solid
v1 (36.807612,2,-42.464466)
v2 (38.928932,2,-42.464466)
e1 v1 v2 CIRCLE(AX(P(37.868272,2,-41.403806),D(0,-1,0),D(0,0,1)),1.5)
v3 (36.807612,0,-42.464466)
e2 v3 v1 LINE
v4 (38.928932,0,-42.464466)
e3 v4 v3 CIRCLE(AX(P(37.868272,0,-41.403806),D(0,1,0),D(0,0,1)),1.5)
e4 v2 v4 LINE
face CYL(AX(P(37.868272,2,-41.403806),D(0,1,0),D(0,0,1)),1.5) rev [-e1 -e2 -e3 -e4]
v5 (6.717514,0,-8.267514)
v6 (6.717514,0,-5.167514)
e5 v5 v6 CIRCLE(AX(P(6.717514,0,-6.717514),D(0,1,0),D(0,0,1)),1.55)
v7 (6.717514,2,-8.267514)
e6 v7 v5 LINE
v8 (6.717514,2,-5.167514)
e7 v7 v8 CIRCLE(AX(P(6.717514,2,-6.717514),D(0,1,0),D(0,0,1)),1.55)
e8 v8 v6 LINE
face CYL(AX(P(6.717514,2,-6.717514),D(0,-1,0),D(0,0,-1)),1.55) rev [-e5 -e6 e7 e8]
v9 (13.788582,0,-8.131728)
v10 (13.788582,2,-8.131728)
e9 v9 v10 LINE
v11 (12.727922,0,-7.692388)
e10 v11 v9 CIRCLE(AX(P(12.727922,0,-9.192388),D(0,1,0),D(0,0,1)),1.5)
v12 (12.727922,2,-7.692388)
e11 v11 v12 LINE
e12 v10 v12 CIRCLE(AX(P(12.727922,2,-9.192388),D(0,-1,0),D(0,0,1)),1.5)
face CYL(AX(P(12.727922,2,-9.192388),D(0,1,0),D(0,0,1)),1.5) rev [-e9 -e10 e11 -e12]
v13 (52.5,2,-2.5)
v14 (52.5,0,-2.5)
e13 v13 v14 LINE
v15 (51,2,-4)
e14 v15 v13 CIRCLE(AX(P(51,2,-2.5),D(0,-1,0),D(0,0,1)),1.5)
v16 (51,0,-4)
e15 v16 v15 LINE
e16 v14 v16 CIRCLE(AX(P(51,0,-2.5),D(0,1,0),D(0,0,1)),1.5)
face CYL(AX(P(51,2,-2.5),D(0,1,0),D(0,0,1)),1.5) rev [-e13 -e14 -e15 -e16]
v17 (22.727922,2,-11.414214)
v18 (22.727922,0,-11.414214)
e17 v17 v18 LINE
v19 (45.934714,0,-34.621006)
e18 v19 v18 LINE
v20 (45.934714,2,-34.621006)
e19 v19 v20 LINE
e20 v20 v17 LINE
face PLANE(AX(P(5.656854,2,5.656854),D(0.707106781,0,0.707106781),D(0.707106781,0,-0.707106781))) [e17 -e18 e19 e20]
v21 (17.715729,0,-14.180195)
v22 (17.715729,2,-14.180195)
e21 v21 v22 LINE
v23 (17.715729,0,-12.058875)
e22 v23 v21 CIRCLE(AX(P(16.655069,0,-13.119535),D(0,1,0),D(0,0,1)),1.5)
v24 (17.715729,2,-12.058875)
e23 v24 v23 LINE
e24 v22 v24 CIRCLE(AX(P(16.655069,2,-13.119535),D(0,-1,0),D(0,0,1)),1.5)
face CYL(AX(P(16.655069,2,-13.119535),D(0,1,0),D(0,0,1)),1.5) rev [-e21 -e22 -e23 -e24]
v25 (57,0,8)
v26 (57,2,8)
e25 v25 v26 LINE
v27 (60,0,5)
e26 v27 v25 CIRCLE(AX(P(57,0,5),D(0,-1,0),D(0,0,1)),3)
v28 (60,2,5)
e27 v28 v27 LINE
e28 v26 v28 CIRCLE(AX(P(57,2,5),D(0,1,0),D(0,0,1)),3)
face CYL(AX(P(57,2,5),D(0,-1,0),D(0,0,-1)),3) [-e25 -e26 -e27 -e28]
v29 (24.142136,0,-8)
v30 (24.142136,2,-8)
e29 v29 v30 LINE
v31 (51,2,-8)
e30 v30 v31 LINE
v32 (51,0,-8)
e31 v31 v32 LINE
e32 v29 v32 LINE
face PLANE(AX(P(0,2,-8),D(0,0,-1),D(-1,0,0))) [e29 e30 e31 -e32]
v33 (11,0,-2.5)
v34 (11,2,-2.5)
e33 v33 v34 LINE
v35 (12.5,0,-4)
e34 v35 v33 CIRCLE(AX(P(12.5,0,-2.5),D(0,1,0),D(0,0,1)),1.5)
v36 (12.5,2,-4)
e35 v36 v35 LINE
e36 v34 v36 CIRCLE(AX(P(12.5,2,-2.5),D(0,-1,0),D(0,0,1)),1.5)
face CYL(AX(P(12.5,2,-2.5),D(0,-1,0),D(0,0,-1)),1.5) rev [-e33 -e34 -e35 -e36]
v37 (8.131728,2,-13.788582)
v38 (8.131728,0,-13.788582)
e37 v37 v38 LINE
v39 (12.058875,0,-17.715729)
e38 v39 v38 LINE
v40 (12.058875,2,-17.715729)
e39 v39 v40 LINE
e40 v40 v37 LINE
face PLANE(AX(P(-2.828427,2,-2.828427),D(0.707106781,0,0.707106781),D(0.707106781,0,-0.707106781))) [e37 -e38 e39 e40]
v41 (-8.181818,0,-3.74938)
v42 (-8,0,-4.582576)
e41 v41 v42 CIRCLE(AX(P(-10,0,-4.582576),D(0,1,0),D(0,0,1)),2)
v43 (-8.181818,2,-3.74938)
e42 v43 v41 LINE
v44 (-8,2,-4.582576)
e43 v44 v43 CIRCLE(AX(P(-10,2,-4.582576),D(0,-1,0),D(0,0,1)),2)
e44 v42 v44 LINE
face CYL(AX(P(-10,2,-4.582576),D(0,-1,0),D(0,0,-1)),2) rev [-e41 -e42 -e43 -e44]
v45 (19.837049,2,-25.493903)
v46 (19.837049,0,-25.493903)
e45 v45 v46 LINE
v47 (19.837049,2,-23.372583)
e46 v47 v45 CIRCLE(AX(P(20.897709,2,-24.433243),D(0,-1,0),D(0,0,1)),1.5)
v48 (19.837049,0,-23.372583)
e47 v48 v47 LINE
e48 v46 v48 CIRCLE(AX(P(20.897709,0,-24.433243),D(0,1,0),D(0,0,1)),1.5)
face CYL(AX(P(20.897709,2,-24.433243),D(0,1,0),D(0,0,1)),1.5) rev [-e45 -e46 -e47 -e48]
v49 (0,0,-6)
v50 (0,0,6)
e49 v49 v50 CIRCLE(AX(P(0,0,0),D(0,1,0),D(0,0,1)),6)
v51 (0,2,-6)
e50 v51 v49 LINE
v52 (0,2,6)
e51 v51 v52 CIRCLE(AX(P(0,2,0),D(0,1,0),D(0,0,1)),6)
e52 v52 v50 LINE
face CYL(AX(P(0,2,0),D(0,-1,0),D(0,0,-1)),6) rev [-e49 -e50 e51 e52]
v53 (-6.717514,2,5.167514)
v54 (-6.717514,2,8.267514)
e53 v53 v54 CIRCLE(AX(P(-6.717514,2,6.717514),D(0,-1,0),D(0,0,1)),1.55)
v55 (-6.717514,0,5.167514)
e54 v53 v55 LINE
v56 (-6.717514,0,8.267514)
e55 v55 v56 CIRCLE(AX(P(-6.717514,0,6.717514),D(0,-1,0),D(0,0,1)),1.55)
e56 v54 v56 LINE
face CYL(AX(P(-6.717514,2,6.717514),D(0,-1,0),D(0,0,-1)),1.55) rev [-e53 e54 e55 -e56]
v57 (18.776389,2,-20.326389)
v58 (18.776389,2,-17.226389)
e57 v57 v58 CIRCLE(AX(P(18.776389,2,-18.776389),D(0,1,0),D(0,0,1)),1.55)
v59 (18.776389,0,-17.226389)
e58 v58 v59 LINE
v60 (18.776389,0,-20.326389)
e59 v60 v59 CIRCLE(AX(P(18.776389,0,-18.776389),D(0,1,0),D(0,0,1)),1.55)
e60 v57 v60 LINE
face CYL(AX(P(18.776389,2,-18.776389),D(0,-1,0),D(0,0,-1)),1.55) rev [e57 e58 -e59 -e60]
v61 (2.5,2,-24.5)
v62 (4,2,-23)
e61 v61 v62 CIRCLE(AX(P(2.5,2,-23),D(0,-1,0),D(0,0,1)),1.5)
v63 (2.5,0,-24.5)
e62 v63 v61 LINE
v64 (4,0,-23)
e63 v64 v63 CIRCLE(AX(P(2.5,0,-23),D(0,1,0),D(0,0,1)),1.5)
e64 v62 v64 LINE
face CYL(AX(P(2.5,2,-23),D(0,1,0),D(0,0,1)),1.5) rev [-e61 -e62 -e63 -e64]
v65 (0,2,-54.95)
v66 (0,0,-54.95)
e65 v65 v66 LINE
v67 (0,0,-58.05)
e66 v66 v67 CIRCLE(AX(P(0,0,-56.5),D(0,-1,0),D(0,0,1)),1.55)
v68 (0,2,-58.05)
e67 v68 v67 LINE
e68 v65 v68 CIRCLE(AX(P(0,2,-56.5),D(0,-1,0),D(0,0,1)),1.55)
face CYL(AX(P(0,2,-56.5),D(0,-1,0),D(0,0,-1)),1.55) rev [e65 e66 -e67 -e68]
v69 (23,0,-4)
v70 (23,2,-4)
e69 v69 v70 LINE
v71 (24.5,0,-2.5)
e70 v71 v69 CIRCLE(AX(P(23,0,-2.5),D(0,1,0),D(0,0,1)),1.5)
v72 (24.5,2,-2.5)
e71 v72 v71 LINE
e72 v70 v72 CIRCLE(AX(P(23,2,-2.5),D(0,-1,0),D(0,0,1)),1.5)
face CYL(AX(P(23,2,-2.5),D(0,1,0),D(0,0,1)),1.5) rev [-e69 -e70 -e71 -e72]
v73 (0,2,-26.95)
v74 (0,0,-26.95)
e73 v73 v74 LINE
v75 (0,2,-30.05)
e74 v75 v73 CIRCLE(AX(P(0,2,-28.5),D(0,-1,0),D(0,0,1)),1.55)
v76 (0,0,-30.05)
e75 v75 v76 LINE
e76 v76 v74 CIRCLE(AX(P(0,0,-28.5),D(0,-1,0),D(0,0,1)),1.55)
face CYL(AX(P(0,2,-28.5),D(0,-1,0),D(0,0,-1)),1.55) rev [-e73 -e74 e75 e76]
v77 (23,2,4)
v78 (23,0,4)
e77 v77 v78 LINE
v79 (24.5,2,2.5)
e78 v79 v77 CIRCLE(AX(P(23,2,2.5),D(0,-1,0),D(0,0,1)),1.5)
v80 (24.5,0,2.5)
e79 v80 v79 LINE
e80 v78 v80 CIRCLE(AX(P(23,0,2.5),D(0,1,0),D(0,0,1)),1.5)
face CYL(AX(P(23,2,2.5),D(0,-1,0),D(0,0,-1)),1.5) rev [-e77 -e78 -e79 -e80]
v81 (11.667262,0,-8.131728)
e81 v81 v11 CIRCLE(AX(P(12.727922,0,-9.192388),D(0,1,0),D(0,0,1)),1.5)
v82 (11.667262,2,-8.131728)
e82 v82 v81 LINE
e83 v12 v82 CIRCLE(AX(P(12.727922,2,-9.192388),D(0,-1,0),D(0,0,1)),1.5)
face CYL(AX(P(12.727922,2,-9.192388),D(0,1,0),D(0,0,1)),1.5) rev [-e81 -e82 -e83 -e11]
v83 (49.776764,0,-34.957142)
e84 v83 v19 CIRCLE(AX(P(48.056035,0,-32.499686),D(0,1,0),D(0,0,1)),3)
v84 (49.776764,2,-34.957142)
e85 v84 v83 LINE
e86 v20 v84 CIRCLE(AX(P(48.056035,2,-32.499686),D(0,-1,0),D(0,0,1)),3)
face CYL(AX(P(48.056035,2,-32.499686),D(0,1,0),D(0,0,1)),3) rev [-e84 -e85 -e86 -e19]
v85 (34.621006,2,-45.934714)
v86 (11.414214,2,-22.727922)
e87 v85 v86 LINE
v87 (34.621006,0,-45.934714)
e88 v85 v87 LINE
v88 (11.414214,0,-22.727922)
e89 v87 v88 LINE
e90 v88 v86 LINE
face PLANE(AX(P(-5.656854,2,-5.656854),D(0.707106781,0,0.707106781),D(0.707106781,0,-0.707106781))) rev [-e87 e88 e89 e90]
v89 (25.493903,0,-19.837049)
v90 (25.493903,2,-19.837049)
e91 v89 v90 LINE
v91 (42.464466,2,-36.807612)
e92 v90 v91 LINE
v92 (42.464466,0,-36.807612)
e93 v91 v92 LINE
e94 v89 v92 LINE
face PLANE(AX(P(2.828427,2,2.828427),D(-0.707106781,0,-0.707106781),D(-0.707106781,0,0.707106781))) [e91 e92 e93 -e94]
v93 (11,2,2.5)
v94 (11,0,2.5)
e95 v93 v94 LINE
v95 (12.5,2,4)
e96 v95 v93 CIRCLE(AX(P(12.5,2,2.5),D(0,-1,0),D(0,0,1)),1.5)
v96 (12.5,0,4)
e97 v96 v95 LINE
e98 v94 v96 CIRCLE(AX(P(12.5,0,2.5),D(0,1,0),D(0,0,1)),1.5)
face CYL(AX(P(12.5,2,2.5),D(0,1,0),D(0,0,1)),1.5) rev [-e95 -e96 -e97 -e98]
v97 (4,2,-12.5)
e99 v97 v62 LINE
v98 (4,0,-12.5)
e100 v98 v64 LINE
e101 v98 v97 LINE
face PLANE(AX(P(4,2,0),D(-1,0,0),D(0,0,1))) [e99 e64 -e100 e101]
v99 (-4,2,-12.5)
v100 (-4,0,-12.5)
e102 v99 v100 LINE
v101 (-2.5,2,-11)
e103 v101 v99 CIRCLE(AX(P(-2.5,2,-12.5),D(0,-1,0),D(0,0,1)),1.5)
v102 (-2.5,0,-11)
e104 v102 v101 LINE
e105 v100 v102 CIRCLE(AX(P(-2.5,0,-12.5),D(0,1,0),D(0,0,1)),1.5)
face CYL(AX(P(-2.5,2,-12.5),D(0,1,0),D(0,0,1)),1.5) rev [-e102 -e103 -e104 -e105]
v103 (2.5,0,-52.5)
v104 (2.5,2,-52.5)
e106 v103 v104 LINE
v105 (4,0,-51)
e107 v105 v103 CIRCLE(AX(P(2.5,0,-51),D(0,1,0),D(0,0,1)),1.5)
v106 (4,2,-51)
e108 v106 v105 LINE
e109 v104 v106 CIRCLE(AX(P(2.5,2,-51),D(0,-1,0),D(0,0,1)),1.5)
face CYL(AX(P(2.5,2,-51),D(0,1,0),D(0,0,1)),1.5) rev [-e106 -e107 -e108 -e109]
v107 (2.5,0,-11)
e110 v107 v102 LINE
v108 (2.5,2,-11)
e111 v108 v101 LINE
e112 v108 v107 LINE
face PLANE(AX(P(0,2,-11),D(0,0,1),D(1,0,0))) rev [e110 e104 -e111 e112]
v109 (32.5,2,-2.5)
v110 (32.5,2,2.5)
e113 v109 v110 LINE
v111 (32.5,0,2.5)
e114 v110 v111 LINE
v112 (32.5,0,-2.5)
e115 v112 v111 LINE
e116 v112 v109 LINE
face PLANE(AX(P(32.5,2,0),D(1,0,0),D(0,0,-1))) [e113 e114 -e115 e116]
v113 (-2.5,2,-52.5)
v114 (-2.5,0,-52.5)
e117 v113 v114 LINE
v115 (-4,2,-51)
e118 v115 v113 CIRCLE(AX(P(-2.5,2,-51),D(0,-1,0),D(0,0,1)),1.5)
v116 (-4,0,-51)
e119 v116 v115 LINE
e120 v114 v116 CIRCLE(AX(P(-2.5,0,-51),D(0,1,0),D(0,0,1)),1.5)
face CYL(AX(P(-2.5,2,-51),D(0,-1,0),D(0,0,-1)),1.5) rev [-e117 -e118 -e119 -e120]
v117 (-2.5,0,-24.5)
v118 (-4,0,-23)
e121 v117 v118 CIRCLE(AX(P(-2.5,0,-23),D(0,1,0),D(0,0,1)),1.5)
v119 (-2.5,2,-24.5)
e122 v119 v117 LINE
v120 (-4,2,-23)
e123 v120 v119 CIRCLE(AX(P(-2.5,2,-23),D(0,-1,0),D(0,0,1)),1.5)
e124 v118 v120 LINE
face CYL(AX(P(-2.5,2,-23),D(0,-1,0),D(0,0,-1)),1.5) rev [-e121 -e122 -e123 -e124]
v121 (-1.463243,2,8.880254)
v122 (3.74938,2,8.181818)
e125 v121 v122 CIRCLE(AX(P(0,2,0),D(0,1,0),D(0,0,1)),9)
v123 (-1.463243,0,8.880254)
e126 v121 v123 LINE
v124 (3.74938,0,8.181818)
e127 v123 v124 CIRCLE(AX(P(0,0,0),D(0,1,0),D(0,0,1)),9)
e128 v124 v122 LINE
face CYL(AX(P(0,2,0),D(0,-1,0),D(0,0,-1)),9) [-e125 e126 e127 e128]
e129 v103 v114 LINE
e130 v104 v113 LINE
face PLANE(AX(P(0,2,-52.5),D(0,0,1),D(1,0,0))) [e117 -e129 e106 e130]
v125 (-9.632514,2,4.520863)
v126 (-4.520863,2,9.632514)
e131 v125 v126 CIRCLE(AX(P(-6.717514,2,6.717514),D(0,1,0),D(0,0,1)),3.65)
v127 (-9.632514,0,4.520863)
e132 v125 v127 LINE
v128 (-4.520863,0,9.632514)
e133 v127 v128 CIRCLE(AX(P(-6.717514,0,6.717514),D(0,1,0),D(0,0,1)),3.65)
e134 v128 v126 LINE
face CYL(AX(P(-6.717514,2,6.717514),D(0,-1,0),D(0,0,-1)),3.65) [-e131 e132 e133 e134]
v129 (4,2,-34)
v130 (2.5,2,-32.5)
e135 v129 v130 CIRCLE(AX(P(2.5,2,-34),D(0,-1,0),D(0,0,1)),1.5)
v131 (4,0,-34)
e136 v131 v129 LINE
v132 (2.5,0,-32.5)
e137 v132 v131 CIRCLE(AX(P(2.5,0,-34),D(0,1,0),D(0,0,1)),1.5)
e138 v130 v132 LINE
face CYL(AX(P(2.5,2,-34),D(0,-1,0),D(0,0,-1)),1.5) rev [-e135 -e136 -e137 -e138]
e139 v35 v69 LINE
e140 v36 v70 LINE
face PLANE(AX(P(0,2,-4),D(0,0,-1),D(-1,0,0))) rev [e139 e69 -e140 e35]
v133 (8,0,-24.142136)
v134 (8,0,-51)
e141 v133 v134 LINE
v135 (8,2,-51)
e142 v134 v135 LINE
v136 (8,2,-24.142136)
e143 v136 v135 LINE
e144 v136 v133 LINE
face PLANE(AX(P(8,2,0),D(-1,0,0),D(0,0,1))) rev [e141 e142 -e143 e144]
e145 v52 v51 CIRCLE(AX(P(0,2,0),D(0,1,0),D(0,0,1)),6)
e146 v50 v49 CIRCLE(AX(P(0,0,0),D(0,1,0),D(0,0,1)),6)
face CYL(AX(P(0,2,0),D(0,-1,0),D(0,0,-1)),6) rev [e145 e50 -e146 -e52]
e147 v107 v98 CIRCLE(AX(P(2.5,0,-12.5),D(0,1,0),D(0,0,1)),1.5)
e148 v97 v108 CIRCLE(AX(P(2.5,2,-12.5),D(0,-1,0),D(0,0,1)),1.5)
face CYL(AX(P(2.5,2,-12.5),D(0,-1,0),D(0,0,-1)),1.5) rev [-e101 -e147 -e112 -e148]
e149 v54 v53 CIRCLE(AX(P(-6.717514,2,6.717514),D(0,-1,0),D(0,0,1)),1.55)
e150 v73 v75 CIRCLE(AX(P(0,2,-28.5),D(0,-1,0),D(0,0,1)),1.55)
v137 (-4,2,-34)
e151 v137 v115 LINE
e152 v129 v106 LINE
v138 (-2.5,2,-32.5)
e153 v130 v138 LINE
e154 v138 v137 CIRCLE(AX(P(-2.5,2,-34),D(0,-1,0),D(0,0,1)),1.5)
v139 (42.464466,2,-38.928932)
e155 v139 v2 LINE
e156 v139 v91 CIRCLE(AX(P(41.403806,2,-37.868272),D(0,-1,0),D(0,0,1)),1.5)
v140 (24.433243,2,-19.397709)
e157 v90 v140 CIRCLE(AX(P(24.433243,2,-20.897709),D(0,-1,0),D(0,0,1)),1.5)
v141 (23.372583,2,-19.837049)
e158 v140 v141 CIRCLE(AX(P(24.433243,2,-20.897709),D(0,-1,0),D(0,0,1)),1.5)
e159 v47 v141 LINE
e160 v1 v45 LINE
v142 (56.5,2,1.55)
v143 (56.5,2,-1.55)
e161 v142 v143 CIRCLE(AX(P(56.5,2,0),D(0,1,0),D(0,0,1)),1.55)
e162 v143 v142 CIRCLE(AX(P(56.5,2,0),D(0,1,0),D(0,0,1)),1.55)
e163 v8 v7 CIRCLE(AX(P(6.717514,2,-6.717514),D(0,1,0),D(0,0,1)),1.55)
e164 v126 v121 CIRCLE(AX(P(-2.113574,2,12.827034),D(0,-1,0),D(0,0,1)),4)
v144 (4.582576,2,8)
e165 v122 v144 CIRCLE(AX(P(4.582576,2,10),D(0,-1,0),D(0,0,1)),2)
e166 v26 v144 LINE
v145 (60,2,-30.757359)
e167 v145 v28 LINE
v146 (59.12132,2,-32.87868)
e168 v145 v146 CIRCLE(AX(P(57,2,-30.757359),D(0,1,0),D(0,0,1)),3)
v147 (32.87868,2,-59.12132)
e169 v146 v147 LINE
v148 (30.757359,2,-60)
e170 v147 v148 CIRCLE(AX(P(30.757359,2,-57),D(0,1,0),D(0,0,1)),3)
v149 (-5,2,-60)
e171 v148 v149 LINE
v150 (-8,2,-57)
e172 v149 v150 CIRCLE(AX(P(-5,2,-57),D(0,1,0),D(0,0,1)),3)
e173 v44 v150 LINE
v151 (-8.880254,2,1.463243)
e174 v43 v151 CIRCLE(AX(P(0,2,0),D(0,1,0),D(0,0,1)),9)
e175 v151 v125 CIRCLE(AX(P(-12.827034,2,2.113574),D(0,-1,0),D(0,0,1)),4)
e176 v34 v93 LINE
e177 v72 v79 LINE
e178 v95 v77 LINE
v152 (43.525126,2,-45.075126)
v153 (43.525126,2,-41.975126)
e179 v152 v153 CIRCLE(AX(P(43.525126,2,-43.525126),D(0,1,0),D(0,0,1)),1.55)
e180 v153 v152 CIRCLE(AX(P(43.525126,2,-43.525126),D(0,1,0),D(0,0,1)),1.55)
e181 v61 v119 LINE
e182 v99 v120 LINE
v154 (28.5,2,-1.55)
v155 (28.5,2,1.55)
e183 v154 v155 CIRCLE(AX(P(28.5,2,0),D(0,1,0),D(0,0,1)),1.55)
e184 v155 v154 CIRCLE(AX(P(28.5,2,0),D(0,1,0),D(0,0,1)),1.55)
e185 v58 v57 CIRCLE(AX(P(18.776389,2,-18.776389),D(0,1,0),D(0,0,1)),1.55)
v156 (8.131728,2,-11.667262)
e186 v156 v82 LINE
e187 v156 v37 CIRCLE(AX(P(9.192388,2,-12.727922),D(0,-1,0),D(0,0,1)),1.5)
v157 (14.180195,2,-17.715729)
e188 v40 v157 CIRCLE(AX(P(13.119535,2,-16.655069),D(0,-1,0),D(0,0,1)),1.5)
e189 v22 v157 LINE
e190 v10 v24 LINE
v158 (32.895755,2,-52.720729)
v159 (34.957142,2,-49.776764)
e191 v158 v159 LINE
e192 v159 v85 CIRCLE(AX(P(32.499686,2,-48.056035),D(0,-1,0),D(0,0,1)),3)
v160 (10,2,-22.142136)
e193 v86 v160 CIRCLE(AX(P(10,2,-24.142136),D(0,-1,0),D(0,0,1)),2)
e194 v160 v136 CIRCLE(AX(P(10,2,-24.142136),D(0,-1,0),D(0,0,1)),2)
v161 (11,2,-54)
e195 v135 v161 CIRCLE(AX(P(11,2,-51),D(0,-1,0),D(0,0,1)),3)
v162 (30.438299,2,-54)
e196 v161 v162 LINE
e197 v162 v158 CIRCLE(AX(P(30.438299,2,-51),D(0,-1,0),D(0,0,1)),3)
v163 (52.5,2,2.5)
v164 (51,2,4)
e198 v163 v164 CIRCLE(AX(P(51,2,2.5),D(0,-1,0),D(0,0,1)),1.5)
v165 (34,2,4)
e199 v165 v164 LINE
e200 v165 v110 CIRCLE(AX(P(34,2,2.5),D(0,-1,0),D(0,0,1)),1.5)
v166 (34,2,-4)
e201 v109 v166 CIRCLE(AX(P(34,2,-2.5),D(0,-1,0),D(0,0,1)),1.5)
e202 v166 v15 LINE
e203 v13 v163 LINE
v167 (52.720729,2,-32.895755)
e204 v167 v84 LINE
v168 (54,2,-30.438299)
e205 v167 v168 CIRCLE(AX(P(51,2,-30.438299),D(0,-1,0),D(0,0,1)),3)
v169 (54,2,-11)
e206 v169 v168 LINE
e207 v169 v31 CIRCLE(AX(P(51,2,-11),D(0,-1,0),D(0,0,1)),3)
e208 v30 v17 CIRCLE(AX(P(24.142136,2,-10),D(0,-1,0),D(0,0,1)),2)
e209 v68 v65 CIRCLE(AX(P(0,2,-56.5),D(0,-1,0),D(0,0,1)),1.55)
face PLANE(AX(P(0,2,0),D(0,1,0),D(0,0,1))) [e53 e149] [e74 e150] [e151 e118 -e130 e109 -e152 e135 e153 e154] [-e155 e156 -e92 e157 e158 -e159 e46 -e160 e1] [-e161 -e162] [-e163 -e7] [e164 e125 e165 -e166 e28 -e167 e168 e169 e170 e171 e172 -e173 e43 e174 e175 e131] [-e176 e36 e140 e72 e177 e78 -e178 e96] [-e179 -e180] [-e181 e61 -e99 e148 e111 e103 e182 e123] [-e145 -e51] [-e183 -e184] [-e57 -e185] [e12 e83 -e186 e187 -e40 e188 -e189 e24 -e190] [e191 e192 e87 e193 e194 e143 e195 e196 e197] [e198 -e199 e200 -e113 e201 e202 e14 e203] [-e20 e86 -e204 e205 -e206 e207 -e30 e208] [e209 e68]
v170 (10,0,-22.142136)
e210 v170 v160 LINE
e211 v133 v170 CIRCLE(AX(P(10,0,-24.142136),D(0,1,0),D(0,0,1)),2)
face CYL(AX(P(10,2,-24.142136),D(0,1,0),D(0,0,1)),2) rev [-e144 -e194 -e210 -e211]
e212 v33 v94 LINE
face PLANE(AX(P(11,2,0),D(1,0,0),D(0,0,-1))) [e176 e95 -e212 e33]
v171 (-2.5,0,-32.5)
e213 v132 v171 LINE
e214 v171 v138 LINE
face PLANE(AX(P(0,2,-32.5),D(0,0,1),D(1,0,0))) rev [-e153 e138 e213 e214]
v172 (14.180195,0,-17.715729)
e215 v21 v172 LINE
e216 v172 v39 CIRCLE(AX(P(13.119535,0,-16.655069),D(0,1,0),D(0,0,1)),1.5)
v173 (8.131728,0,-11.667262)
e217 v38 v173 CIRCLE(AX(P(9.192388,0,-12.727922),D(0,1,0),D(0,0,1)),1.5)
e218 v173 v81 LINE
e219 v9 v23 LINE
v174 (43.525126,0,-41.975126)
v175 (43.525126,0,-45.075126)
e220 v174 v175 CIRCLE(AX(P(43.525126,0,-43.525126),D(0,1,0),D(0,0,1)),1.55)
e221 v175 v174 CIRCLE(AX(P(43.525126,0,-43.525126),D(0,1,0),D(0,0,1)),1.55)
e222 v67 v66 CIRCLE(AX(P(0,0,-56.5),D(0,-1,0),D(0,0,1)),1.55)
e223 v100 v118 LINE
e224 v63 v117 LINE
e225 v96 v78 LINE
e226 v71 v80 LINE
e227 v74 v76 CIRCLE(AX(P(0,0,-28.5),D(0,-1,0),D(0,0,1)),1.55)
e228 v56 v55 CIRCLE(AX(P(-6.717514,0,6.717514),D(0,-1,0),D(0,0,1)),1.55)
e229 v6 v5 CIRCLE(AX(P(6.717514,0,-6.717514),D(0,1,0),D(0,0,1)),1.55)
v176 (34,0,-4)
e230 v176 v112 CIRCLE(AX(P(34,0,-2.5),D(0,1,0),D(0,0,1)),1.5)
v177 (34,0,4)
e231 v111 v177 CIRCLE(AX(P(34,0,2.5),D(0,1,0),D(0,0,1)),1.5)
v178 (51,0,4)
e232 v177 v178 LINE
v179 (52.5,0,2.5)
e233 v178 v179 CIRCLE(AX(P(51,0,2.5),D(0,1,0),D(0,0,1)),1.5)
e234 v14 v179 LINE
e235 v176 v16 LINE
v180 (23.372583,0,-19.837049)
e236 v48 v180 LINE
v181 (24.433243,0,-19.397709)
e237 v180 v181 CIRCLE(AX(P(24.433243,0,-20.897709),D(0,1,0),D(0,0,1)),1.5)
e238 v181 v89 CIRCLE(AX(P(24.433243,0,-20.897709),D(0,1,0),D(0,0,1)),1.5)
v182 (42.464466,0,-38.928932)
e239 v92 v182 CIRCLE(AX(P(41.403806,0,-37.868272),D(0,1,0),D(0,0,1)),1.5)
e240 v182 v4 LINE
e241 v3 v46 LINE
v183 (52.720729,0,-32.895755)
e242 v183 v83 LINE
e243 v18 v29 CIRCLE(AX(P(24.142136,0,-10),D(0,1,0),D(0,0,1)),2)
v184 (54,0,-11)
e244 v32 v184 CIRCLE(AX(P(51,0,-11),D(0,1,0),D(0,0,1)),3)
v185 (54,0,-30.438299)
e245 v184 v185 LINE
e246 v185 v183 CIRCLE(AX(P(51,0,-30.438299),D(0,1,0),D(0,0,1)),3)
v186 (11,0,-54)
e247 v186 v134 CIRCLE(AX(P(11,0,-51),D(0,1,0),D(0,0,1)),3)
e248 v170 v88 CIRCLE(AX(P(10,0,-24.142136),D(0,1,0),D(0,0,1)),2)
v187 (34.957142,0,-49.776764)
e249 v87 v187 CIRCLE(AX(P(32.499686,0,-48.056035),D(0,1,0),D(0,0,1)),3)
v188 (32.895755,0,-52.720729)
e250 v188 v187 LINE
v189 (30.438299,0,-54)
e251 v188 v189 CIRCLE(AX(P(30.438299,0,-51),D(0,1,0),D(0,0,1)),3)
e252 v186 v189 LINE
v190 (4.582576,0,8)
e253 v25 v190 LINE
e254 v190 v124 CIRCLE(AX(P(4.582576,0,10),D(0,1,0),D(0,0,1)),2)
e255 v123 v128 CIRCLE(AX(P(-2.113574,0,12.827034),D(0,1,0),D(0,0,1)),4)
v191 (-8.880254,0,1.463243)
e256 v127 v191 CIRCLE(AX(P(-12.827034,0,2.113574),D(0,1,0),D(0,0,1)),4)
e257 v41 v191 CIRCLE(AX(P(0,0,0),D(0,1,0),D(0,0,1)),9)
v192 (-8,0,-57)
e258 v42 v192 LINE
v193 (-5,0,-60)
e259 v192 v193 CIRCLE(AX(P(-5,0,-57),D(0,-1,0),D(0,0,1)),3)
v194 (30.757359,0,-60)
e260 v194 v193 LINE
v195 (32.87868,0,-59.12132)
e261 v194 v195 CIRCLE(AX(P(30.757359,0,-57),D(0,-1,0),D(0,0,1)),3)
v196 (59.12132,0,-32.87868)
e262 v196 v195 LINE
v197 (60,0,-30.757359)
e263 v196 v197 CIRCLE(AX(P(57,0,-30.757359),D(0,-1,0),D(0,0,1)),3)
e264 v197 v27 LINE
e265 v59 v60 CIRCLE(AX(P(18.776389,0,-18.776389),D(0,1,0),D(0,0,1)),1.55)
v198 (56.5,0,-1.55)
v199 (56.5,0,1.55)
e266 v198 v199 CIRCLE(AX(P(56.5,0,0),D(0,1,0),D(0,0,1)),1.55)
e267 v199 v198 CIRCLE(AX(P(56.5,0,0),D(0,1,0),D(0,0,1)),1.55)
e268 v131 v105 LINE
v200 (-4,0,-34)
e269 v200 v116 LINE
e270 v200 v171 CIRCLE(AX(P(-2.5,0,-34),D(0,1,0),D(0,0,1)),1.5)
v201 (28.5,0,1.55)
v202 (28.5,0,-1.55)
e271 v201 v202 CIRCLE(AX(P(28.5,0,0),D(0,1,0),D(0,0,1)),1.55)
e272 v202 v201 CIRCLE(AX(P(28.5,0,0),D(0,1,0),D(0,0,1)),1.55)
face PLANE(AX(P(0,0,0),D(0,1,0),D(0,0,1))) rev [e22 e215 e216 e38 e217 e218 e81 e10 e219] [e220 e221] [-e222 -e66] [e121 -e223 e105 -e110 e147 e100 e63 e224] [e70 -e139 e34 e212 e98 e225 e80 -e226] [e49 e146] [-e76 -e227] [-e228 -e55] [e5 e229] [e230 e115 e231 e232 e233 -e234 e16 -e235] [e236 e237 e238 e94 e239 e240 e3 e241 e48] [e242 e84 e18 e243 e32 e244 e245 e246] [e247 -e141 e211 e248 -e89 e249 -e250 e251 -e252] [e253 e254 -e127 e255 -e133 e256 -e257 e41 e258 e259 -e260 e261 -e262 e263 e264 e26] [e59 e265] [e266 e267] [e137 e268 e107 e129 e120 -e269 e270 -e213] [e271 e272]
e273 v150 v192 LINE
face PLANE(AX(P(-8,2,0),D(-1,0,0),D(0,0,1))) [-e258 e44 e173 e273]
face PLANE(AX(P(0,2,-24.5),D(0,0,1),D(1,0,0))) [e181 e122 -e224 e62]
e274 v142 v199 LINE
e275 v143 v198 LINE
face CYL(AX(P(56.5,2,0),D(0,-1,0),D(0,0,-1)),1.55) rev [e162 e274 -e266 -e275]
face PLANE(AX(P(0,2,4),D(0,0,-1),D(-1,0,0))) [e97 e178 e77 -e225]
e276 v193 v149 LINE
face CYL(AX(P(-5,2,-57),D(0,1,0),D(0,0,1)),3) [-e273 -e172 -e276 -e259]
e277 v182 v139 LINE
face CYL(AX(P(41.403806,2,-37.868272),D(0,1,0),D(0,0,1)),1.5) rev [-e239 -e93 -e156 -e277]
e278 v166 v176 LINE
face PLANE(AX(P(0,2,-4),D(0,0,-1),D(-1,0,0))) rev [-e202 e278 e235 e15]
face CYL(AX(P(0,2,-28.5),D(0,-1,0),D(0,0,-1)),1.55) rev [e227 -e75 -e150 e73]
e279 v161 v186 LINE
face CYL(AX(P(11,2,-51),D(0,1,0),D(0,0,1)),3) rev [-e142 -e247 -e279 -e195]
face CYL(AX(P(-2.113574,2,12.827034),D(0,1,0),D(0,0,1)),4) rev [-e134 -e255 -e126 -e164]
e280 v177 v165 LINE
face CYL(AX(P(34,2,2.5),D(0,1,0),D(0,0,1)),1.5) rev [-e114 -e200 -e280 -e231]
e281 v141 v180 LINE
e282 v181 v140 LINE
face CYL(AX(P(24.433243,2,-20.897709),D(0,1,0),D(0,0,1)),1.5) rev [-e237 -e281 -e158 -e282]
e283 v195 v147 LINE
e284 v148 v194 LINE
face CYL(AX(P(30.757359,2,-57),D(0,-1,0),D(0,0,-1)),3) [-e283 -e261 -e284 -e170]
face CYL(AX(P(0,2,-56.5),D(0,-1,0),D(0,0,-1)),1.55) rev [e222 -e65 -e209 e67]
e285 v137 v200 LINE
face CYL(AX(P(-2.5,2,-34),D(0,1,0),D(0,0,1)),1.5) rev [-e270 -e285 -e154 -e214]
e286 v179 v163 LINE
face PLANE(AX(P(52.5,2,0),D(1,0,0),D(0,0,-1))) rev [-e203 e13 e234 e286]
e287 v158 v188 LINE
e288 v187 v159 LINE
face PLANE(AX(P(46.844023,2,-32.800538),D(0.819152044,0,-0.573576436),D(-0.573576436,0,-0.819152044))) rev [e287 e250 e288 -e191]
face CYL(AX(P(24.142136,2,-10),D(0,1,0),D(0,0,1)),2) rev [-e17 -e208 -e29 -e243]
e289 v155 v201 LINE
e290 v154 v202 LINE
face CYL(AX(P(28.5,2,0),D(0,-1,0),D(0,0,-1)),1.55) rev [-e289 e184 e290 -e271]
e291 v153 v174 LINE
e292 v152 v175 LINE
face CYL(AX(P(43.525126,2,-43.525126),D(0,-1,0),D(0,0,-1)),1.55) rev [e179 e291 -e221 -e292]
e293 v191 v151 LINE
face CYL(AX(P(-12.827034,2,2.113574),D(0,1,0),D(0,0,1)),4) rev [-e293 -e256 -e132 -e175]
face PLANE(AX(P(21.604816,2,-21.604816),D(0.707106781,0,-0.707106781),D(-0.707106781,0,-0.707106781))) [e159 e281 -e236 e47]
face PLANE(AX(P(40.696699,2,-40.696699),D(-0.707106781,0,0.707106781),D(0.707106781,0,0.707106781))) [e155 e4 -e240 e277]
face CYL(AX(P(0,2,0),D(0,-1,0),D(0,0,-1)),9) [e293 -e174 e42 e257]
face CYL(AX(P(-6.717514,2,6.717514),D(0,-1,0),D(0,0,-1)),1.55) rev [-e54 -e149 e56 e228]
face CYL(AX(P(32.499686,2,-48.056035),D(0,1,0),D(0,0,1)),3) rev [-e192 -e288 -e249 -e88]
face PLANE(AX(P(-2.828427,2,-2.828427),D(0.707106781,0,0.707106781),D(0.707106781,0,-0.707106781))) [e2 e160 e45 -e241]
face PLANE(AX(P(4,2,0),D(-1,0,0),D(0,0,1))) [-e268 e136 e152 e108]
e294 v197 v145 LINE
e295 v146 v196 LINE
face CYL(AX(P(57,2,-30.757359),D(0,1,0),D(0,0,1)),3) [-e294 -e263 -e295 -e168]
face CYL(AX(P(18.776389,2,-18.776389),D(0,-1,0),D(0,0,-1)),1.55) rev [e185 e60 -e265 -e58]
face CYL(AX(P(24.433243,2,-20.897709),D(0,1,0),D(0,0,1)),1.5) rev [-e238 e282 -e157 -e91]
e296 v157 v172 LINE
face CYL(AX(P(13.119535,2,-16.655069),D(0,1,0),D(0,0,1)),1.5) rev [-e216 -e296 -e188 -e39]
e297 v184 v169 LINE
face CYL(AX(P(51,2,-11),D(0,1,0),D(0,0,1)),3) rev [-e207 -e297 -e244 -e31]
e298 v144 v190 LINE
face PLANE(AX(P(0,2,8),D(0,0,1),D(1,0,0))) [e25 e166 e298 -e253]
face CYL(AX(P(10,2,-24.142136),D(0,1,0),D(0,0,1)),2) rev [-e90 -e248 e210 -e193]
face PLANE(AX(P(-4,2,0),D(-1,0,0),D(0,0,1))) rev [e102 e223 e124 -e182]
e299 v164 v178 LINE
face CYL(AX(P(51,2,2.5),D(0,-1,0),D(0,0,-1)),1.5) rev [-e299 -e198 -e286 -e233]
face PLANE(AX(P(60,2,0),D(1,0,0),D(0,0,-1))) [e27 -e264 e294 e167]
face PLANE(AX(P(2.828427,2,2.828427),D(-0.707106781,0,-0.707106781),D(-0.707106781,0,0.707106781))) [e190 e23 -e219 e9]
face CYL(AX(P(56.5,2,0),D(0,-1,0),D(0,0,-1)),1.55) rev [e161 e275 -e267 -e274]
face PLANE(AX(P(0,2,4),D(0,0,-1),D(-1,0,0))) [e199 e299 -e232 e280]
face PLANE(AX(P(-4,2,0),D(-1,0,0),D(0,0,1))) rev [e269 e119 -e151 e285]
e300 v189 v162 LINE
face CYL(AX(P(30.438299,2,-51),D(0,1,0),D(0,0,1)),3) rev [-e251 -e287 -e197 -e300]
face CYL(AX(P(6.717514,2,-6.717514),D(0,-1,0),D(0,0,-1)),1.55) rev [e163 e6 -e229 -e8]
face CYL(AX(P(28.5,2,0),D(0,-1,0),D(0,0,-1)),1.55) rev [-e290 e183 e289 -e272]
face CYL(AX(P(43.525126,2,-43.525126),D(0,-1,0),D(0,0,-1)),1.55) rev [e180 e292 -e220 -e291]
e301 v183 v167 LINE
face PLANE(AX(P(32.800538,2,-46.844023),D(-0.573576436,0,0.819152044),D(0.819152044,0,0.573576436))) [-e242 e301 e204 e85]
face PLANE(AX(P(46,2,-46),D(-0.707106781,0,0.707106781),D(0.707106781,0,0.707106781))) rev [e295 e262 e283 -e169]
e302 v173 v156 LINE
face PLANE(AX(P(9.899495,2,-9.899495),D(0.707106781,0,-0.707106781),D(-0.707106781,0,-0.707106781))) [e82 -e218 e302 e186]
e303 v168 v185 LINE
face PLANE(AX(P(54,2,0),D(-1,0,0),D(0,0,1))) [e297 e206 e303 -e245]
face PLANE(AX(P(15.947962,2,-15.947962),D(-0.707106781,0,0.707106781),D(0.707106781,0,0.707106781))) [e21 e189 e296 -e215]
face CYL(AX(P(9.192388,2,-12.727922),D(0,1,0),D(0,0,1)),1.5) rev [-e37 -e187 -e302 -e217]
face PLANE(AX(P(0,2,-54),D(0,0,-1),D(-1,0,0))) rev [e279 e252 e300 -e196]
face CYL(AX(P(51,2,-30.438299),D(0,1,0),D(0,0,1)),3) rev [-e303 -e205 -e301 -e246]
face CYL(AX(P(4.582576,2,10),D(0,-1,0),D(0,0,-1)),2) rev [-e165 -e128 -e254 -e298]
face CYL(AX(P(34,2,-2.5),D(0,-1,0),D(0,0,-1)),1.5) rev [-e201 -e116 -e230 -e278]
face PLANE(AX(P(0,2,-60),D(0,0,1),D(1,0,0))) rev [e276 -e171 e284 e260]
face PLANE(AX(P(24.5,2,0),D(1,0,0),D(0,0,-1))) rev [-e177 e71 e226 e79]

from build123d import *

# Parameters (mm, degrees)
SKETCH_1_R      = 6
SKETCH_1_R_2    = 1.55
SKETCH_1_W      = 13.5
SKETCH_1_H      = 8
SKETCH_1_W_2    = 8
SKETCH_1_H_2    = 13.5
SKETCH_1_W_3    = 20
SKETCH_1_H_3    = 20
EXTRUDE_1_DEPTH = 2
FILLET_1_R      = 2
FILLET_2_R      = 1.5
FILLET_3_R      = 3
FILLET_4_R      = 4


with BuildPart() as part:
    # 草图1 → 凸台-拉伸1 (new body)
    with BuildSketch(Plane(origin=(0, 0, 0), x_dir=(1, 0, 0), z_dir=(0, 1, 0))):
        with BuildLine():
            Line((4.123105626, -8), (60, -8))
            Line((60, -8), (60, 32))
            Line((60, 32), (32, 60))
            Line((32, 60), (-8, 60))
            Line((-8, 60), (-8, 4.123105626))
            ThreePointArc((-8, 4.123105626), (-8.992056265, 0.378053083), (-8.317851846, -3.437054068))
            ThreePointArc((-8.317851846, -3.437054068), (-9.298454173, -9.298454173), (-3.437054068, -8.317851846))
            ThreePointArc((-3.437054068, -8.317851846), (0.378053083, -8.992056265), (4.123105626, -8))
        make_face()
        with Locations(Location((0, 0, 0), (0, 0, 270))):
            Circle(SKETCH_1_R, mode=Mode.SUBTRACT)
        with Locations(Location((6.717514421, 6.717514421, 0), (0, 0, 270))):
            Circle(SKETCH_1_R_2, mode=Mode.SUBTRACT)
        with Locations((17.75, 0)):
            Rectangle(SKETCH_1_W, SKETCH_1_H, mode=Mode.SUBTRACT)
        with Locations((0, 17.75)):
            Rectangle(SKETCH_1_W_2, SKETCH_1_H_2, mode=Mode.SUBTRACT)
        Polygon((12.727922061, 7.071067812), (7.071067812, 12.727922061), (13.119534675, 18.776388924), (18.776388924, 13.119534675), align=None, mode=Mode.SUBTRACT)
        with Locations(Location((18.776388924, 18.776388924, 0), (0, 0, 270))):
            Circle(SKETCH_1_R_2, mode=Mode.SUBTRACT)
        with Locations(Location((28.5, 0, 0), (0, 0, 270))):
            Circle(SKETCH_1_R_2, mode=Mode.SUBTRACT)
        with Locations((42.5, 0)):
            Rectangle(SKETCH_1_W_3, SKETCH_1_H, mode=Mode.SUBTRACT)
        with Locations(Location((56.5, 0, 0), (0, 0, 270))):
            Circle(SKETCH_1_R_2, mode=Mode.SUBTRACT)
        Polygon((54, 8), (19.313708499, 8), (47.714713492, 36.401004993), (54, 32), align=None, mode=Mode.SUBTRACT)
        with Locations(Location((0, 28.5, 0), (0, 0, 270))):
            Circle(SKETCH_1_R_2, mode=Mode.SUBTRACT)
        Polygon((36.401004993, 47.714713492), (8, 19.313708499), (8, 54), (32, 54), align=None, mode=Mode.SUBTRACT)
        with Locations((0, 42.5)):
            Rectangle(SKETCH_1_W_2, SKETCH_1_H_3, mode=Mode.SUBTRACT)
        with Locations(Location((0, 56.5, 0), (0, 0, 270))):
            Circle(SKETCH_1_R_2, mode=Mode.SUBTRACT)
        Polygon((24.433243174, 18.776388924), (18.776388924, 24.433243174), (37.868272016, 43.525126266), (43.525126266, 37.868272016), align=None, mode=Mode.SUBTRACT)
        with Locations(Location((43.525126266, 43.525126266, 0), (0, 0, 270))):
            Circle(SKETCH_1_R_2, mode=Mode.SUBTRACT)
        with Locations(Location((-6.717514421, -6.717514421, 0), (0, 0, 270))):
            Circle(SKETCH_1_R_2, mode=Mode.SUBTRACT)
    extrude(amount=EXTRUDE_1_DEPTH)

    # 圆角1
    fillet_1_edges = [part.edges().sort_by_distance(p)[0] for p in [
        (19.313708499, 1, -8),
        (8, 1, -19.313708499),
        (-8, 1, -4.123105626),
        (4.123105626, 1, 8),
    ]]
    fillet(fillet_1_edges, radius=FILLET_1_R)

    # 圆角2
    fillet_2_edges = [part.edges().sort_by_distance(p)[0] for p in [
        (7.071067812, 1, -12.727922061),
        (12.727922061, 1, -7.071067812),
        (18.776388924, 1, -13.119534675),
        (13.119534675, 1, -18.776388924),
        (18.776388924, 1, -24.433243174),
        (24.433243174, 1, -18.776388924),
        (43.525126266, 1, -37.868272016),
        (37.868272016, 1, -43.525126266),
        (32.5, 1, -4),
        (32.5, 1, 4),
        (52.5, 1, 4),
        (52.5, 1, -4),
        (11, 1, -4),
        (11, 1, 4),
        (24.5, 1, 4),
        (24.5, 1, -4),
        (4, 1, -52.5),
        (-4, 1, -52.5),
        (-4, 1, -32.5),
        (4, 1, -32.5),
        (4, 1, -11),
        (4, 1, -24.5),
        (-4, 1, -24.5),
        (-4, 1, -11),
    ]]
    fillet(fillet_2_edges, radius=FILLET_2_R)

    # 圆角3
    fillet_3_edges = [part.edges().sort_by_distance(p)[0] for p in [
        (54, 1, -8),
        (54, 1, -32),
        (47.714713492, 1, -36.401004993),
        (36.401004993, 1, -47.714713492),
        (32, 1, -54),
        (8, 1, -54),
        (-8, 1, -60),
        (32, 1, -60),
        (60, 1, -32),
        (60, 1, 8),
    ]]
    fillet(fillet_3_edges, radius=FILLET_3_R)

    # 圆角4
    fillet_4_edges = [part.edges().sort_by_distance(p)[0] for p in [
        (-8.317851846, 1, 3.437054068),
        (-3.437054068, 1, 8.317851846),
    ]]
    fillet(fillet_4_edges, radius=FILLET_4_R)


solid = part.part
